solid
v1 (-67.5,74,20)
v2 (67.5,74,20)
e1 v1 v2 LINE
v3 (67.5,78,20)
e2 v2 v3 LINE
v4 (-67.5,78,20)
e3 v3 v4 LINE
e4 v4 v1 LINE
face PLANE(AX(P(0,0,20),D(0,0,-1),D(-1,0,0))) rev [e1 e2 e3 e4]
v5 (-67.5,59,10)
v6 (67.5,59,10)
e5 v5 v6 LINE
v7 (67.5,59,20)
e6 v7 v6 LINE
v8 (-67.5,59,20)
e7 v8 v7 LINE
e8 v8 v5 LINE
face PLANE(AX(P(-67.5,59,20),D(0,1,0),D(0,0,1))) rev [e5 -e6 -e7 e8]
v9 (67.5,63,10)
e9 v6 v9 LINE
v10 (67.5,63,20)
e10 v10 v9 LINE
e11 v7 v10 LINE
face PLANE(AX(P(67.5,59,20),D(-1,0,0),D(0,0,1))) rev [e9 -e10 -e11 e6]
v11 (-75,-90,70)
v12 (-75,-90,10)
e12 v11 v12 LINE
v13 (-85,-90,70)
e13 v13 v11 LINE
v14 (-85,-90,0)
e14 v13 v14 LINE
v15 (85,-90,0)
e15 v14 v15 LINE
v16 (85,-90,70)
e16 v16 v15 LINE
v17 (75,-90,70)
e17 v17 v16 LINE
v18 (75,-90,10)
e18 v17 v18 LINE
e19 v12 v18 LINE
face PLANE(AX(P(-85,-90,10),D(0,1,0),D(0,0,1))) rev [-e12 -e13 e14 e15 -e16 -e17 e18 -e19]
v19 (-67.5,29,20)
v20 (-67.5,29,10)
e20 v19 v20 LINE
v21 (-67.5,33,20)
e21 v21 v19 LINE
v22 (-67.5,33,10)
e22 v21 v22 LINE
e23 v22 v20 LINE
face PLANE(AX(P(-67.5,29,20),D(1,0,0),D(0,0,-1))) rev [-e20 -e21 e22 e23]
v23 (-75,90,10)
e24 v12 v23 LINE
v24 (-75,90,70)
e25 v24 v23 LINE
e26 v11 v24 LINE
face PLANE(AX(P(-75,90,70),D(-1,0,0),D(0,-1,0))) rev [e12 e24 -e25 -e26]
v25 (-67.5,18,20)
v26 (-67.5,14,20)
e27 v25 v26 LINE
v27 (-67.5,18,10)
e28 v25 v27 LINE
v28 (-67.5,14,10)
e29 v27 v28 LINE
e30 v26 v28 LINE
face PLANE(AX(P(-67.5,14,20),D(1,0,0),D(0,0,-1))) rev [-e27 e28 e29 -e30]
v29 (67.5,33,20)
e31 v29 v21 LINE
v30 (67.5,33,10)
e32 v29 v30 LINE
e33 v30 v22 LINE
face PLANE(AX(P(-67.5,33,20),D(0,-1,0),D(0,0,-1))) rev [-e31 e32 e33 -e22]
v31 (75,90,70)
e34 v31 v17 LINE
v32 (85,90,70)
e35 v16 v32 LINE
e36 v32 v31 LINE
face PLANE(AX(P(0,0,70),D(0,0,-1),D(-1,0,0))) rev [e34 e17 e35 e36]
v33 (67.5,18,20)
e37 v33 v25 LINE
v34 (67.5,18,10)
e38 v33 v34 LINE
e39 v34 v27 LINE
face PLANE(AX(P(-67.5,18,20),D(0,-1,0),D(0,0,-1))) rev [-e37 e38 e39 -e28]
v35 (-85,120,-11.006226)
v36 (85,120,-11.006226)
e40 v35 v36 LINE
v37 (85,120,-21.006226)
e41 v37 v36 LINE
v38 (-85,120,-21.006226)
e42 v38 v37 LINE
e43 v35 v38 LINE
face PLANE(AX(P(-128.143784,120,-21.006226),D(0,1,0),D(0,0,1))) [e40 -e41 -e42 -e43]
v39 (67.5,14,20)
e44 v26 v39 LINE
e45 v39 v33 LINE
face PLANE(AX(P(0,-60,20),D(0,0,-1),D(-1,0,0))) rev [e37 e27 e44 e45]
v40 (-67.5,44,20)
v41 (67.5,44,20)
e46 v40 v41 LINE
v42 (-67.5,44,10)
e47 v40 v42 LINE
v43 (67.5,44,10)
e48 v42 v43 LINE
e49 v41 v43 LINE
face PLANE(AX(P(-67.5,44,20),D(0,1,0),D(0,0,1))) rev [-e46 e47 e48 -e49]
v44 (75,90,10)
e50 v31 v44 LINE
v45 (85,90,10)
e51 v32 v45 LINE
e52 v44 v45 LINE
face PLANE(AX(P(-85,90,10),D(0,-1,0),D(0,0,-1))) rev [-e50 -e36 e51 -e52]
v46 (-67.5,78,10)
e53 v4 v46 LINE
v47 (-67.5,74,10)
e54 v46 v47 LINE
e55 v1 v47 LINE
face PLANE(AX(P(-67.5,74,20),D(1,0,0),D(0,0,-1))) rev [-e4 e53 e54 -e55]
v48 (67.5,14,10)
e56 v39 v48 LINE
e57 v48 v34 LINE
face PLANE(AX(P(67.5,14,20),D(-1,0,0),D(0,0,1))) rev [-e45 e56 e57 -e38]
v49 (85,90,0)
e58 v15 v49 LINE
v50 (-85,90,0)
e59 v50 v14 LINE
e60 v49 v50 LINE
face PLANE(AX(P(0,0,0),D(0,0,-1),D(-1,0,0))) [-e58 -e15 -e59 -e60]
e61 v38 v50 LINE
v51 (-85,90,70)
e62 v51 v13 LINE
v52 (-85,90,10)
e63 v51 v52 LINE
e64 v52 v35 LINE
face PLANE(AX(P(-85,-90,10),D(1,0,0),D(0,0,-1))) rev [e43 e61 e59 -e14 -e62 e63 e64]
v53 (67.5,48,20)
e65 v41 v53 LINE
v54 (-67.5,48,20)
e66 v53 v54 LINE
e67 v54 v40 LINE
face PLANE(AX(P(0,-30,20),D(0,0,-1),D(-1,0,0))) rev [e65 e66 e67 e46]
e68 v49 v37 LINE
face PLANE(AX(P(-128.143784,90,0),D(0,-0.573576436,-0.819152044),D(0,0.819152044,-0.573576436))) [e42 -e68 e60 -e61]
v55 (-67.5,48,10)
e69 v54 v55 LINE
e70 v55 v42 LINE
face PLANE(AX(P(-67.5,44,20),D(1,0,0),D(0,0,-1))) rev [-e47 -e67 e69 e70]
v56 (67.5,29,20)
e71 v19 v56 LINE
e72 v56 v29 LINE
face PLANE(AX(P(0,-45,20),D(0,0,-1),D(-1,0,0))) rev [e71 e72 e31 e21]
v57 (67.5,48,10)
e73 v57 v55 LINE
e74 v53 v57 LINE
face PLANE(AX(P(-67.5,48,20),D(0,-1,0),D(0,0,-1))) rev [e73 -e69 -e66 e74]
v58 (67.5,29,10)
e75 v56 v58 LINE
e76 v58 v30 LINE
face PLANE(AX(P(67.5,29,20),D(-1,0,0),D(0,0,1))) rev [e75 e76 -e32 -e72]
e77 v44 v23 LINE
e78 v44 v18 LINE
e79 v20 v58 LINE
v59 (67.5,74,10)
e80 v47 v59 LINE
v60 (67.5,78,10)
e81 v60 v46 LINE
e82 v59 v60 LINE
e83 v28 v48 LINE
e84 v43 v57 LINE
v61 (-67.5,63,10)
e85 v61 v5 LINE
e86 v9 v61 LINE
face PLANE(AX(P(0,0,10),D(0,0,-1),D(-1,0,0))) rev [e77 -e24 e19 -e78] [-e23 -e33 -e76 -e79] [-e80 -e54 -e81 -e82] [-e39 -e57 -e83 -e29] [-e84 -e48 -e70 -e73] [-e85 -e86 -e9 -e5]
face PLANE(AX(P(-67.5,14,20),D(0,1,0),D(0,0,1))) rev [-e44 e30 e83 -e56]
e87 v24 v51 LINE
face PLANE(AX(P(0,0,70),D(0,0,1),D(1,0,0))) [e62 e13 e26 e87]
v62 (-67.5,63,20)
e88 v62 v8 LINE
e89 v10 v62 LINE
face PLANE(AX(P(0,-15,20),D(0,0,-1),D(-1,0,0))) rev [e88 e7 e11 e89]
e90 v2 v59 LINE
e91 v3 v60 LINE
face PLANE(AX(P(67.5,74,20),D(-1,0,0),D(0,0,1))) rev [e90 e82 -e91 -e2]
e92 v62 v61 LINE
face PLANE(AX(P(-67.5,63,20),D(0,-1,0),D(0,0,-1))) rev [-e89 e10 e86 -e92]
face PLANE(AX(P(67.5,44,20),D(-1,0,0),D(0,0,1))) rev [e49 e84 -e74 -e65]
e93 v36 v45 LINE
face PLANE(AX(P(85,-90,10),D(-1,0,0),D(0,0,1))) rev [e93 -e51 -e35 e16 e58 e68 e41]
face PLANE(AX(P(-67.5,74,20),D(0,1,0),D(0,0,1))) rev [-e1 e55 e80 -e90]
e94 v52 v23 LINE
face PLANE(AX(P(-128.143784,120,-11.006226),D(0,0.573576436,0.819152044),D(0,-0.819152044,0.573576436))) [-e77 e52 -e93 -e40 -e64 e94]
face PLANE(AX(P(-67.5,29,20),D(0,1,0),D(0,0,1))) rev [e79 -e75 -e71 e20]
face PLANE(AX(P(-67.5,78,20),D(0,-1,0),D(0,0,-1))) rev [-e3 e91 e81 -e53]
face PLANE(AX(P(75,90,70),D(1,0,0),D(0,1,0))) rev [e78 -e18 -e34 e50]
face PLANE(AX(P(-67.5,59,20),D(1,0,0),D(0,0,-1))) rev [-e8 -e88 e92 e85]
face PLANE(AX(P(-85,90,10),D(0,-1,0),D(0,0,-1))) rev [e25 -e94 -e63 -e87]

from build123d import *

# Parameters (mm, degrees)
SKETCH_1_W             = 170
SKETCH_1_H             = 180
EXTRUDE_1_DEPTH        = 10
SKETCH_2_W             = 10
SKETCH_2_H             = 180
EXTRUDE_2_DEPTH        = 60
EXTRUDE_3_REACH        = 206.695
SKETCH_4_W             = 135
SKETCH_4_H             = 4
EXTRUDE_4_DEPTH        = 10
PATTERN_LINEAR_1_COUNT = 5
PATTERN_LINEAR_1_PITCH = 15


with BuildPart() as part:
    # 草图1 → 凸台-拉伸1 (new body)
    with BuildSketch(Plane.XY):
        Rectangle(SKETCH_1_W, SKETCH_1_H)
    extrude(amount=EXTRUDE_1_DEPTH)

    # 草图2 → 凸台-拉伸2 (add)
    with BuildSketch(Plane.XY.offset(10)):
        with Locations((-80, 0)):
            Rectangle(SKETCH_2_W, SKETCH_2_H)
        with Locations((80, 0)):
            Rectangle(SKETCH_2_W, SKETCH_2_H)
    extrude(amount=EXTRUDE_2_DEPTH)

    # 凸台-拉伸3: up to this face of the body (flat: up to its plane)
    extrude_3_end = Plane(part.part.faces().sort_by_distance((-85, 0, 35))[0])
    # 草图3 → 凸台-拉伸3 (add, up to the picked face)
    with BuildSketch(Plane(origin=(85, 0, 0), x_dir=(0, 0, -1), z_dir=(1, 0, 0)), mode=Mode.PRIVATE) as extrude_3_sk1:
        Polygon((0, 90), (21.006226146, 120), (11.006226146, 120), (-10, 90), align=None)
    extrude_3_tool1 = split(extrude(extrude_3_sk1.sketch, amount=-EXTRUDE_3_REACH, mode=Mode.PRIVATE), bisect_by=extrude_3_end, keep=Keep.BOTH, mode=Mode.PRIVATE)
    add(extrude_3_tool1.solids().sort_by(Axis((85, 105, -5.503113), (-1, 0, 0)))[0])

    # 草图4 → 凸台-拉伸4 (add)
    with BuildSketch(Plane.XY.offset(10)):
        with Locations((0, 76)):
            Rectangle(SKETCH_4_W, SKETCH_4_H)
    extrude_4 = extrude(amount=EXTRUDE_4_DEPTH)

    # 阵列(线性)1: 凸台-拉伸4 ×5
    with Locations(*[(0, -i * PATTERN_LINEAR_1_PITCH, 0) for i in range(1, PATTERN_LINEAR_1_COUNT)]):
        add(extrude_4)


solid = part.part
